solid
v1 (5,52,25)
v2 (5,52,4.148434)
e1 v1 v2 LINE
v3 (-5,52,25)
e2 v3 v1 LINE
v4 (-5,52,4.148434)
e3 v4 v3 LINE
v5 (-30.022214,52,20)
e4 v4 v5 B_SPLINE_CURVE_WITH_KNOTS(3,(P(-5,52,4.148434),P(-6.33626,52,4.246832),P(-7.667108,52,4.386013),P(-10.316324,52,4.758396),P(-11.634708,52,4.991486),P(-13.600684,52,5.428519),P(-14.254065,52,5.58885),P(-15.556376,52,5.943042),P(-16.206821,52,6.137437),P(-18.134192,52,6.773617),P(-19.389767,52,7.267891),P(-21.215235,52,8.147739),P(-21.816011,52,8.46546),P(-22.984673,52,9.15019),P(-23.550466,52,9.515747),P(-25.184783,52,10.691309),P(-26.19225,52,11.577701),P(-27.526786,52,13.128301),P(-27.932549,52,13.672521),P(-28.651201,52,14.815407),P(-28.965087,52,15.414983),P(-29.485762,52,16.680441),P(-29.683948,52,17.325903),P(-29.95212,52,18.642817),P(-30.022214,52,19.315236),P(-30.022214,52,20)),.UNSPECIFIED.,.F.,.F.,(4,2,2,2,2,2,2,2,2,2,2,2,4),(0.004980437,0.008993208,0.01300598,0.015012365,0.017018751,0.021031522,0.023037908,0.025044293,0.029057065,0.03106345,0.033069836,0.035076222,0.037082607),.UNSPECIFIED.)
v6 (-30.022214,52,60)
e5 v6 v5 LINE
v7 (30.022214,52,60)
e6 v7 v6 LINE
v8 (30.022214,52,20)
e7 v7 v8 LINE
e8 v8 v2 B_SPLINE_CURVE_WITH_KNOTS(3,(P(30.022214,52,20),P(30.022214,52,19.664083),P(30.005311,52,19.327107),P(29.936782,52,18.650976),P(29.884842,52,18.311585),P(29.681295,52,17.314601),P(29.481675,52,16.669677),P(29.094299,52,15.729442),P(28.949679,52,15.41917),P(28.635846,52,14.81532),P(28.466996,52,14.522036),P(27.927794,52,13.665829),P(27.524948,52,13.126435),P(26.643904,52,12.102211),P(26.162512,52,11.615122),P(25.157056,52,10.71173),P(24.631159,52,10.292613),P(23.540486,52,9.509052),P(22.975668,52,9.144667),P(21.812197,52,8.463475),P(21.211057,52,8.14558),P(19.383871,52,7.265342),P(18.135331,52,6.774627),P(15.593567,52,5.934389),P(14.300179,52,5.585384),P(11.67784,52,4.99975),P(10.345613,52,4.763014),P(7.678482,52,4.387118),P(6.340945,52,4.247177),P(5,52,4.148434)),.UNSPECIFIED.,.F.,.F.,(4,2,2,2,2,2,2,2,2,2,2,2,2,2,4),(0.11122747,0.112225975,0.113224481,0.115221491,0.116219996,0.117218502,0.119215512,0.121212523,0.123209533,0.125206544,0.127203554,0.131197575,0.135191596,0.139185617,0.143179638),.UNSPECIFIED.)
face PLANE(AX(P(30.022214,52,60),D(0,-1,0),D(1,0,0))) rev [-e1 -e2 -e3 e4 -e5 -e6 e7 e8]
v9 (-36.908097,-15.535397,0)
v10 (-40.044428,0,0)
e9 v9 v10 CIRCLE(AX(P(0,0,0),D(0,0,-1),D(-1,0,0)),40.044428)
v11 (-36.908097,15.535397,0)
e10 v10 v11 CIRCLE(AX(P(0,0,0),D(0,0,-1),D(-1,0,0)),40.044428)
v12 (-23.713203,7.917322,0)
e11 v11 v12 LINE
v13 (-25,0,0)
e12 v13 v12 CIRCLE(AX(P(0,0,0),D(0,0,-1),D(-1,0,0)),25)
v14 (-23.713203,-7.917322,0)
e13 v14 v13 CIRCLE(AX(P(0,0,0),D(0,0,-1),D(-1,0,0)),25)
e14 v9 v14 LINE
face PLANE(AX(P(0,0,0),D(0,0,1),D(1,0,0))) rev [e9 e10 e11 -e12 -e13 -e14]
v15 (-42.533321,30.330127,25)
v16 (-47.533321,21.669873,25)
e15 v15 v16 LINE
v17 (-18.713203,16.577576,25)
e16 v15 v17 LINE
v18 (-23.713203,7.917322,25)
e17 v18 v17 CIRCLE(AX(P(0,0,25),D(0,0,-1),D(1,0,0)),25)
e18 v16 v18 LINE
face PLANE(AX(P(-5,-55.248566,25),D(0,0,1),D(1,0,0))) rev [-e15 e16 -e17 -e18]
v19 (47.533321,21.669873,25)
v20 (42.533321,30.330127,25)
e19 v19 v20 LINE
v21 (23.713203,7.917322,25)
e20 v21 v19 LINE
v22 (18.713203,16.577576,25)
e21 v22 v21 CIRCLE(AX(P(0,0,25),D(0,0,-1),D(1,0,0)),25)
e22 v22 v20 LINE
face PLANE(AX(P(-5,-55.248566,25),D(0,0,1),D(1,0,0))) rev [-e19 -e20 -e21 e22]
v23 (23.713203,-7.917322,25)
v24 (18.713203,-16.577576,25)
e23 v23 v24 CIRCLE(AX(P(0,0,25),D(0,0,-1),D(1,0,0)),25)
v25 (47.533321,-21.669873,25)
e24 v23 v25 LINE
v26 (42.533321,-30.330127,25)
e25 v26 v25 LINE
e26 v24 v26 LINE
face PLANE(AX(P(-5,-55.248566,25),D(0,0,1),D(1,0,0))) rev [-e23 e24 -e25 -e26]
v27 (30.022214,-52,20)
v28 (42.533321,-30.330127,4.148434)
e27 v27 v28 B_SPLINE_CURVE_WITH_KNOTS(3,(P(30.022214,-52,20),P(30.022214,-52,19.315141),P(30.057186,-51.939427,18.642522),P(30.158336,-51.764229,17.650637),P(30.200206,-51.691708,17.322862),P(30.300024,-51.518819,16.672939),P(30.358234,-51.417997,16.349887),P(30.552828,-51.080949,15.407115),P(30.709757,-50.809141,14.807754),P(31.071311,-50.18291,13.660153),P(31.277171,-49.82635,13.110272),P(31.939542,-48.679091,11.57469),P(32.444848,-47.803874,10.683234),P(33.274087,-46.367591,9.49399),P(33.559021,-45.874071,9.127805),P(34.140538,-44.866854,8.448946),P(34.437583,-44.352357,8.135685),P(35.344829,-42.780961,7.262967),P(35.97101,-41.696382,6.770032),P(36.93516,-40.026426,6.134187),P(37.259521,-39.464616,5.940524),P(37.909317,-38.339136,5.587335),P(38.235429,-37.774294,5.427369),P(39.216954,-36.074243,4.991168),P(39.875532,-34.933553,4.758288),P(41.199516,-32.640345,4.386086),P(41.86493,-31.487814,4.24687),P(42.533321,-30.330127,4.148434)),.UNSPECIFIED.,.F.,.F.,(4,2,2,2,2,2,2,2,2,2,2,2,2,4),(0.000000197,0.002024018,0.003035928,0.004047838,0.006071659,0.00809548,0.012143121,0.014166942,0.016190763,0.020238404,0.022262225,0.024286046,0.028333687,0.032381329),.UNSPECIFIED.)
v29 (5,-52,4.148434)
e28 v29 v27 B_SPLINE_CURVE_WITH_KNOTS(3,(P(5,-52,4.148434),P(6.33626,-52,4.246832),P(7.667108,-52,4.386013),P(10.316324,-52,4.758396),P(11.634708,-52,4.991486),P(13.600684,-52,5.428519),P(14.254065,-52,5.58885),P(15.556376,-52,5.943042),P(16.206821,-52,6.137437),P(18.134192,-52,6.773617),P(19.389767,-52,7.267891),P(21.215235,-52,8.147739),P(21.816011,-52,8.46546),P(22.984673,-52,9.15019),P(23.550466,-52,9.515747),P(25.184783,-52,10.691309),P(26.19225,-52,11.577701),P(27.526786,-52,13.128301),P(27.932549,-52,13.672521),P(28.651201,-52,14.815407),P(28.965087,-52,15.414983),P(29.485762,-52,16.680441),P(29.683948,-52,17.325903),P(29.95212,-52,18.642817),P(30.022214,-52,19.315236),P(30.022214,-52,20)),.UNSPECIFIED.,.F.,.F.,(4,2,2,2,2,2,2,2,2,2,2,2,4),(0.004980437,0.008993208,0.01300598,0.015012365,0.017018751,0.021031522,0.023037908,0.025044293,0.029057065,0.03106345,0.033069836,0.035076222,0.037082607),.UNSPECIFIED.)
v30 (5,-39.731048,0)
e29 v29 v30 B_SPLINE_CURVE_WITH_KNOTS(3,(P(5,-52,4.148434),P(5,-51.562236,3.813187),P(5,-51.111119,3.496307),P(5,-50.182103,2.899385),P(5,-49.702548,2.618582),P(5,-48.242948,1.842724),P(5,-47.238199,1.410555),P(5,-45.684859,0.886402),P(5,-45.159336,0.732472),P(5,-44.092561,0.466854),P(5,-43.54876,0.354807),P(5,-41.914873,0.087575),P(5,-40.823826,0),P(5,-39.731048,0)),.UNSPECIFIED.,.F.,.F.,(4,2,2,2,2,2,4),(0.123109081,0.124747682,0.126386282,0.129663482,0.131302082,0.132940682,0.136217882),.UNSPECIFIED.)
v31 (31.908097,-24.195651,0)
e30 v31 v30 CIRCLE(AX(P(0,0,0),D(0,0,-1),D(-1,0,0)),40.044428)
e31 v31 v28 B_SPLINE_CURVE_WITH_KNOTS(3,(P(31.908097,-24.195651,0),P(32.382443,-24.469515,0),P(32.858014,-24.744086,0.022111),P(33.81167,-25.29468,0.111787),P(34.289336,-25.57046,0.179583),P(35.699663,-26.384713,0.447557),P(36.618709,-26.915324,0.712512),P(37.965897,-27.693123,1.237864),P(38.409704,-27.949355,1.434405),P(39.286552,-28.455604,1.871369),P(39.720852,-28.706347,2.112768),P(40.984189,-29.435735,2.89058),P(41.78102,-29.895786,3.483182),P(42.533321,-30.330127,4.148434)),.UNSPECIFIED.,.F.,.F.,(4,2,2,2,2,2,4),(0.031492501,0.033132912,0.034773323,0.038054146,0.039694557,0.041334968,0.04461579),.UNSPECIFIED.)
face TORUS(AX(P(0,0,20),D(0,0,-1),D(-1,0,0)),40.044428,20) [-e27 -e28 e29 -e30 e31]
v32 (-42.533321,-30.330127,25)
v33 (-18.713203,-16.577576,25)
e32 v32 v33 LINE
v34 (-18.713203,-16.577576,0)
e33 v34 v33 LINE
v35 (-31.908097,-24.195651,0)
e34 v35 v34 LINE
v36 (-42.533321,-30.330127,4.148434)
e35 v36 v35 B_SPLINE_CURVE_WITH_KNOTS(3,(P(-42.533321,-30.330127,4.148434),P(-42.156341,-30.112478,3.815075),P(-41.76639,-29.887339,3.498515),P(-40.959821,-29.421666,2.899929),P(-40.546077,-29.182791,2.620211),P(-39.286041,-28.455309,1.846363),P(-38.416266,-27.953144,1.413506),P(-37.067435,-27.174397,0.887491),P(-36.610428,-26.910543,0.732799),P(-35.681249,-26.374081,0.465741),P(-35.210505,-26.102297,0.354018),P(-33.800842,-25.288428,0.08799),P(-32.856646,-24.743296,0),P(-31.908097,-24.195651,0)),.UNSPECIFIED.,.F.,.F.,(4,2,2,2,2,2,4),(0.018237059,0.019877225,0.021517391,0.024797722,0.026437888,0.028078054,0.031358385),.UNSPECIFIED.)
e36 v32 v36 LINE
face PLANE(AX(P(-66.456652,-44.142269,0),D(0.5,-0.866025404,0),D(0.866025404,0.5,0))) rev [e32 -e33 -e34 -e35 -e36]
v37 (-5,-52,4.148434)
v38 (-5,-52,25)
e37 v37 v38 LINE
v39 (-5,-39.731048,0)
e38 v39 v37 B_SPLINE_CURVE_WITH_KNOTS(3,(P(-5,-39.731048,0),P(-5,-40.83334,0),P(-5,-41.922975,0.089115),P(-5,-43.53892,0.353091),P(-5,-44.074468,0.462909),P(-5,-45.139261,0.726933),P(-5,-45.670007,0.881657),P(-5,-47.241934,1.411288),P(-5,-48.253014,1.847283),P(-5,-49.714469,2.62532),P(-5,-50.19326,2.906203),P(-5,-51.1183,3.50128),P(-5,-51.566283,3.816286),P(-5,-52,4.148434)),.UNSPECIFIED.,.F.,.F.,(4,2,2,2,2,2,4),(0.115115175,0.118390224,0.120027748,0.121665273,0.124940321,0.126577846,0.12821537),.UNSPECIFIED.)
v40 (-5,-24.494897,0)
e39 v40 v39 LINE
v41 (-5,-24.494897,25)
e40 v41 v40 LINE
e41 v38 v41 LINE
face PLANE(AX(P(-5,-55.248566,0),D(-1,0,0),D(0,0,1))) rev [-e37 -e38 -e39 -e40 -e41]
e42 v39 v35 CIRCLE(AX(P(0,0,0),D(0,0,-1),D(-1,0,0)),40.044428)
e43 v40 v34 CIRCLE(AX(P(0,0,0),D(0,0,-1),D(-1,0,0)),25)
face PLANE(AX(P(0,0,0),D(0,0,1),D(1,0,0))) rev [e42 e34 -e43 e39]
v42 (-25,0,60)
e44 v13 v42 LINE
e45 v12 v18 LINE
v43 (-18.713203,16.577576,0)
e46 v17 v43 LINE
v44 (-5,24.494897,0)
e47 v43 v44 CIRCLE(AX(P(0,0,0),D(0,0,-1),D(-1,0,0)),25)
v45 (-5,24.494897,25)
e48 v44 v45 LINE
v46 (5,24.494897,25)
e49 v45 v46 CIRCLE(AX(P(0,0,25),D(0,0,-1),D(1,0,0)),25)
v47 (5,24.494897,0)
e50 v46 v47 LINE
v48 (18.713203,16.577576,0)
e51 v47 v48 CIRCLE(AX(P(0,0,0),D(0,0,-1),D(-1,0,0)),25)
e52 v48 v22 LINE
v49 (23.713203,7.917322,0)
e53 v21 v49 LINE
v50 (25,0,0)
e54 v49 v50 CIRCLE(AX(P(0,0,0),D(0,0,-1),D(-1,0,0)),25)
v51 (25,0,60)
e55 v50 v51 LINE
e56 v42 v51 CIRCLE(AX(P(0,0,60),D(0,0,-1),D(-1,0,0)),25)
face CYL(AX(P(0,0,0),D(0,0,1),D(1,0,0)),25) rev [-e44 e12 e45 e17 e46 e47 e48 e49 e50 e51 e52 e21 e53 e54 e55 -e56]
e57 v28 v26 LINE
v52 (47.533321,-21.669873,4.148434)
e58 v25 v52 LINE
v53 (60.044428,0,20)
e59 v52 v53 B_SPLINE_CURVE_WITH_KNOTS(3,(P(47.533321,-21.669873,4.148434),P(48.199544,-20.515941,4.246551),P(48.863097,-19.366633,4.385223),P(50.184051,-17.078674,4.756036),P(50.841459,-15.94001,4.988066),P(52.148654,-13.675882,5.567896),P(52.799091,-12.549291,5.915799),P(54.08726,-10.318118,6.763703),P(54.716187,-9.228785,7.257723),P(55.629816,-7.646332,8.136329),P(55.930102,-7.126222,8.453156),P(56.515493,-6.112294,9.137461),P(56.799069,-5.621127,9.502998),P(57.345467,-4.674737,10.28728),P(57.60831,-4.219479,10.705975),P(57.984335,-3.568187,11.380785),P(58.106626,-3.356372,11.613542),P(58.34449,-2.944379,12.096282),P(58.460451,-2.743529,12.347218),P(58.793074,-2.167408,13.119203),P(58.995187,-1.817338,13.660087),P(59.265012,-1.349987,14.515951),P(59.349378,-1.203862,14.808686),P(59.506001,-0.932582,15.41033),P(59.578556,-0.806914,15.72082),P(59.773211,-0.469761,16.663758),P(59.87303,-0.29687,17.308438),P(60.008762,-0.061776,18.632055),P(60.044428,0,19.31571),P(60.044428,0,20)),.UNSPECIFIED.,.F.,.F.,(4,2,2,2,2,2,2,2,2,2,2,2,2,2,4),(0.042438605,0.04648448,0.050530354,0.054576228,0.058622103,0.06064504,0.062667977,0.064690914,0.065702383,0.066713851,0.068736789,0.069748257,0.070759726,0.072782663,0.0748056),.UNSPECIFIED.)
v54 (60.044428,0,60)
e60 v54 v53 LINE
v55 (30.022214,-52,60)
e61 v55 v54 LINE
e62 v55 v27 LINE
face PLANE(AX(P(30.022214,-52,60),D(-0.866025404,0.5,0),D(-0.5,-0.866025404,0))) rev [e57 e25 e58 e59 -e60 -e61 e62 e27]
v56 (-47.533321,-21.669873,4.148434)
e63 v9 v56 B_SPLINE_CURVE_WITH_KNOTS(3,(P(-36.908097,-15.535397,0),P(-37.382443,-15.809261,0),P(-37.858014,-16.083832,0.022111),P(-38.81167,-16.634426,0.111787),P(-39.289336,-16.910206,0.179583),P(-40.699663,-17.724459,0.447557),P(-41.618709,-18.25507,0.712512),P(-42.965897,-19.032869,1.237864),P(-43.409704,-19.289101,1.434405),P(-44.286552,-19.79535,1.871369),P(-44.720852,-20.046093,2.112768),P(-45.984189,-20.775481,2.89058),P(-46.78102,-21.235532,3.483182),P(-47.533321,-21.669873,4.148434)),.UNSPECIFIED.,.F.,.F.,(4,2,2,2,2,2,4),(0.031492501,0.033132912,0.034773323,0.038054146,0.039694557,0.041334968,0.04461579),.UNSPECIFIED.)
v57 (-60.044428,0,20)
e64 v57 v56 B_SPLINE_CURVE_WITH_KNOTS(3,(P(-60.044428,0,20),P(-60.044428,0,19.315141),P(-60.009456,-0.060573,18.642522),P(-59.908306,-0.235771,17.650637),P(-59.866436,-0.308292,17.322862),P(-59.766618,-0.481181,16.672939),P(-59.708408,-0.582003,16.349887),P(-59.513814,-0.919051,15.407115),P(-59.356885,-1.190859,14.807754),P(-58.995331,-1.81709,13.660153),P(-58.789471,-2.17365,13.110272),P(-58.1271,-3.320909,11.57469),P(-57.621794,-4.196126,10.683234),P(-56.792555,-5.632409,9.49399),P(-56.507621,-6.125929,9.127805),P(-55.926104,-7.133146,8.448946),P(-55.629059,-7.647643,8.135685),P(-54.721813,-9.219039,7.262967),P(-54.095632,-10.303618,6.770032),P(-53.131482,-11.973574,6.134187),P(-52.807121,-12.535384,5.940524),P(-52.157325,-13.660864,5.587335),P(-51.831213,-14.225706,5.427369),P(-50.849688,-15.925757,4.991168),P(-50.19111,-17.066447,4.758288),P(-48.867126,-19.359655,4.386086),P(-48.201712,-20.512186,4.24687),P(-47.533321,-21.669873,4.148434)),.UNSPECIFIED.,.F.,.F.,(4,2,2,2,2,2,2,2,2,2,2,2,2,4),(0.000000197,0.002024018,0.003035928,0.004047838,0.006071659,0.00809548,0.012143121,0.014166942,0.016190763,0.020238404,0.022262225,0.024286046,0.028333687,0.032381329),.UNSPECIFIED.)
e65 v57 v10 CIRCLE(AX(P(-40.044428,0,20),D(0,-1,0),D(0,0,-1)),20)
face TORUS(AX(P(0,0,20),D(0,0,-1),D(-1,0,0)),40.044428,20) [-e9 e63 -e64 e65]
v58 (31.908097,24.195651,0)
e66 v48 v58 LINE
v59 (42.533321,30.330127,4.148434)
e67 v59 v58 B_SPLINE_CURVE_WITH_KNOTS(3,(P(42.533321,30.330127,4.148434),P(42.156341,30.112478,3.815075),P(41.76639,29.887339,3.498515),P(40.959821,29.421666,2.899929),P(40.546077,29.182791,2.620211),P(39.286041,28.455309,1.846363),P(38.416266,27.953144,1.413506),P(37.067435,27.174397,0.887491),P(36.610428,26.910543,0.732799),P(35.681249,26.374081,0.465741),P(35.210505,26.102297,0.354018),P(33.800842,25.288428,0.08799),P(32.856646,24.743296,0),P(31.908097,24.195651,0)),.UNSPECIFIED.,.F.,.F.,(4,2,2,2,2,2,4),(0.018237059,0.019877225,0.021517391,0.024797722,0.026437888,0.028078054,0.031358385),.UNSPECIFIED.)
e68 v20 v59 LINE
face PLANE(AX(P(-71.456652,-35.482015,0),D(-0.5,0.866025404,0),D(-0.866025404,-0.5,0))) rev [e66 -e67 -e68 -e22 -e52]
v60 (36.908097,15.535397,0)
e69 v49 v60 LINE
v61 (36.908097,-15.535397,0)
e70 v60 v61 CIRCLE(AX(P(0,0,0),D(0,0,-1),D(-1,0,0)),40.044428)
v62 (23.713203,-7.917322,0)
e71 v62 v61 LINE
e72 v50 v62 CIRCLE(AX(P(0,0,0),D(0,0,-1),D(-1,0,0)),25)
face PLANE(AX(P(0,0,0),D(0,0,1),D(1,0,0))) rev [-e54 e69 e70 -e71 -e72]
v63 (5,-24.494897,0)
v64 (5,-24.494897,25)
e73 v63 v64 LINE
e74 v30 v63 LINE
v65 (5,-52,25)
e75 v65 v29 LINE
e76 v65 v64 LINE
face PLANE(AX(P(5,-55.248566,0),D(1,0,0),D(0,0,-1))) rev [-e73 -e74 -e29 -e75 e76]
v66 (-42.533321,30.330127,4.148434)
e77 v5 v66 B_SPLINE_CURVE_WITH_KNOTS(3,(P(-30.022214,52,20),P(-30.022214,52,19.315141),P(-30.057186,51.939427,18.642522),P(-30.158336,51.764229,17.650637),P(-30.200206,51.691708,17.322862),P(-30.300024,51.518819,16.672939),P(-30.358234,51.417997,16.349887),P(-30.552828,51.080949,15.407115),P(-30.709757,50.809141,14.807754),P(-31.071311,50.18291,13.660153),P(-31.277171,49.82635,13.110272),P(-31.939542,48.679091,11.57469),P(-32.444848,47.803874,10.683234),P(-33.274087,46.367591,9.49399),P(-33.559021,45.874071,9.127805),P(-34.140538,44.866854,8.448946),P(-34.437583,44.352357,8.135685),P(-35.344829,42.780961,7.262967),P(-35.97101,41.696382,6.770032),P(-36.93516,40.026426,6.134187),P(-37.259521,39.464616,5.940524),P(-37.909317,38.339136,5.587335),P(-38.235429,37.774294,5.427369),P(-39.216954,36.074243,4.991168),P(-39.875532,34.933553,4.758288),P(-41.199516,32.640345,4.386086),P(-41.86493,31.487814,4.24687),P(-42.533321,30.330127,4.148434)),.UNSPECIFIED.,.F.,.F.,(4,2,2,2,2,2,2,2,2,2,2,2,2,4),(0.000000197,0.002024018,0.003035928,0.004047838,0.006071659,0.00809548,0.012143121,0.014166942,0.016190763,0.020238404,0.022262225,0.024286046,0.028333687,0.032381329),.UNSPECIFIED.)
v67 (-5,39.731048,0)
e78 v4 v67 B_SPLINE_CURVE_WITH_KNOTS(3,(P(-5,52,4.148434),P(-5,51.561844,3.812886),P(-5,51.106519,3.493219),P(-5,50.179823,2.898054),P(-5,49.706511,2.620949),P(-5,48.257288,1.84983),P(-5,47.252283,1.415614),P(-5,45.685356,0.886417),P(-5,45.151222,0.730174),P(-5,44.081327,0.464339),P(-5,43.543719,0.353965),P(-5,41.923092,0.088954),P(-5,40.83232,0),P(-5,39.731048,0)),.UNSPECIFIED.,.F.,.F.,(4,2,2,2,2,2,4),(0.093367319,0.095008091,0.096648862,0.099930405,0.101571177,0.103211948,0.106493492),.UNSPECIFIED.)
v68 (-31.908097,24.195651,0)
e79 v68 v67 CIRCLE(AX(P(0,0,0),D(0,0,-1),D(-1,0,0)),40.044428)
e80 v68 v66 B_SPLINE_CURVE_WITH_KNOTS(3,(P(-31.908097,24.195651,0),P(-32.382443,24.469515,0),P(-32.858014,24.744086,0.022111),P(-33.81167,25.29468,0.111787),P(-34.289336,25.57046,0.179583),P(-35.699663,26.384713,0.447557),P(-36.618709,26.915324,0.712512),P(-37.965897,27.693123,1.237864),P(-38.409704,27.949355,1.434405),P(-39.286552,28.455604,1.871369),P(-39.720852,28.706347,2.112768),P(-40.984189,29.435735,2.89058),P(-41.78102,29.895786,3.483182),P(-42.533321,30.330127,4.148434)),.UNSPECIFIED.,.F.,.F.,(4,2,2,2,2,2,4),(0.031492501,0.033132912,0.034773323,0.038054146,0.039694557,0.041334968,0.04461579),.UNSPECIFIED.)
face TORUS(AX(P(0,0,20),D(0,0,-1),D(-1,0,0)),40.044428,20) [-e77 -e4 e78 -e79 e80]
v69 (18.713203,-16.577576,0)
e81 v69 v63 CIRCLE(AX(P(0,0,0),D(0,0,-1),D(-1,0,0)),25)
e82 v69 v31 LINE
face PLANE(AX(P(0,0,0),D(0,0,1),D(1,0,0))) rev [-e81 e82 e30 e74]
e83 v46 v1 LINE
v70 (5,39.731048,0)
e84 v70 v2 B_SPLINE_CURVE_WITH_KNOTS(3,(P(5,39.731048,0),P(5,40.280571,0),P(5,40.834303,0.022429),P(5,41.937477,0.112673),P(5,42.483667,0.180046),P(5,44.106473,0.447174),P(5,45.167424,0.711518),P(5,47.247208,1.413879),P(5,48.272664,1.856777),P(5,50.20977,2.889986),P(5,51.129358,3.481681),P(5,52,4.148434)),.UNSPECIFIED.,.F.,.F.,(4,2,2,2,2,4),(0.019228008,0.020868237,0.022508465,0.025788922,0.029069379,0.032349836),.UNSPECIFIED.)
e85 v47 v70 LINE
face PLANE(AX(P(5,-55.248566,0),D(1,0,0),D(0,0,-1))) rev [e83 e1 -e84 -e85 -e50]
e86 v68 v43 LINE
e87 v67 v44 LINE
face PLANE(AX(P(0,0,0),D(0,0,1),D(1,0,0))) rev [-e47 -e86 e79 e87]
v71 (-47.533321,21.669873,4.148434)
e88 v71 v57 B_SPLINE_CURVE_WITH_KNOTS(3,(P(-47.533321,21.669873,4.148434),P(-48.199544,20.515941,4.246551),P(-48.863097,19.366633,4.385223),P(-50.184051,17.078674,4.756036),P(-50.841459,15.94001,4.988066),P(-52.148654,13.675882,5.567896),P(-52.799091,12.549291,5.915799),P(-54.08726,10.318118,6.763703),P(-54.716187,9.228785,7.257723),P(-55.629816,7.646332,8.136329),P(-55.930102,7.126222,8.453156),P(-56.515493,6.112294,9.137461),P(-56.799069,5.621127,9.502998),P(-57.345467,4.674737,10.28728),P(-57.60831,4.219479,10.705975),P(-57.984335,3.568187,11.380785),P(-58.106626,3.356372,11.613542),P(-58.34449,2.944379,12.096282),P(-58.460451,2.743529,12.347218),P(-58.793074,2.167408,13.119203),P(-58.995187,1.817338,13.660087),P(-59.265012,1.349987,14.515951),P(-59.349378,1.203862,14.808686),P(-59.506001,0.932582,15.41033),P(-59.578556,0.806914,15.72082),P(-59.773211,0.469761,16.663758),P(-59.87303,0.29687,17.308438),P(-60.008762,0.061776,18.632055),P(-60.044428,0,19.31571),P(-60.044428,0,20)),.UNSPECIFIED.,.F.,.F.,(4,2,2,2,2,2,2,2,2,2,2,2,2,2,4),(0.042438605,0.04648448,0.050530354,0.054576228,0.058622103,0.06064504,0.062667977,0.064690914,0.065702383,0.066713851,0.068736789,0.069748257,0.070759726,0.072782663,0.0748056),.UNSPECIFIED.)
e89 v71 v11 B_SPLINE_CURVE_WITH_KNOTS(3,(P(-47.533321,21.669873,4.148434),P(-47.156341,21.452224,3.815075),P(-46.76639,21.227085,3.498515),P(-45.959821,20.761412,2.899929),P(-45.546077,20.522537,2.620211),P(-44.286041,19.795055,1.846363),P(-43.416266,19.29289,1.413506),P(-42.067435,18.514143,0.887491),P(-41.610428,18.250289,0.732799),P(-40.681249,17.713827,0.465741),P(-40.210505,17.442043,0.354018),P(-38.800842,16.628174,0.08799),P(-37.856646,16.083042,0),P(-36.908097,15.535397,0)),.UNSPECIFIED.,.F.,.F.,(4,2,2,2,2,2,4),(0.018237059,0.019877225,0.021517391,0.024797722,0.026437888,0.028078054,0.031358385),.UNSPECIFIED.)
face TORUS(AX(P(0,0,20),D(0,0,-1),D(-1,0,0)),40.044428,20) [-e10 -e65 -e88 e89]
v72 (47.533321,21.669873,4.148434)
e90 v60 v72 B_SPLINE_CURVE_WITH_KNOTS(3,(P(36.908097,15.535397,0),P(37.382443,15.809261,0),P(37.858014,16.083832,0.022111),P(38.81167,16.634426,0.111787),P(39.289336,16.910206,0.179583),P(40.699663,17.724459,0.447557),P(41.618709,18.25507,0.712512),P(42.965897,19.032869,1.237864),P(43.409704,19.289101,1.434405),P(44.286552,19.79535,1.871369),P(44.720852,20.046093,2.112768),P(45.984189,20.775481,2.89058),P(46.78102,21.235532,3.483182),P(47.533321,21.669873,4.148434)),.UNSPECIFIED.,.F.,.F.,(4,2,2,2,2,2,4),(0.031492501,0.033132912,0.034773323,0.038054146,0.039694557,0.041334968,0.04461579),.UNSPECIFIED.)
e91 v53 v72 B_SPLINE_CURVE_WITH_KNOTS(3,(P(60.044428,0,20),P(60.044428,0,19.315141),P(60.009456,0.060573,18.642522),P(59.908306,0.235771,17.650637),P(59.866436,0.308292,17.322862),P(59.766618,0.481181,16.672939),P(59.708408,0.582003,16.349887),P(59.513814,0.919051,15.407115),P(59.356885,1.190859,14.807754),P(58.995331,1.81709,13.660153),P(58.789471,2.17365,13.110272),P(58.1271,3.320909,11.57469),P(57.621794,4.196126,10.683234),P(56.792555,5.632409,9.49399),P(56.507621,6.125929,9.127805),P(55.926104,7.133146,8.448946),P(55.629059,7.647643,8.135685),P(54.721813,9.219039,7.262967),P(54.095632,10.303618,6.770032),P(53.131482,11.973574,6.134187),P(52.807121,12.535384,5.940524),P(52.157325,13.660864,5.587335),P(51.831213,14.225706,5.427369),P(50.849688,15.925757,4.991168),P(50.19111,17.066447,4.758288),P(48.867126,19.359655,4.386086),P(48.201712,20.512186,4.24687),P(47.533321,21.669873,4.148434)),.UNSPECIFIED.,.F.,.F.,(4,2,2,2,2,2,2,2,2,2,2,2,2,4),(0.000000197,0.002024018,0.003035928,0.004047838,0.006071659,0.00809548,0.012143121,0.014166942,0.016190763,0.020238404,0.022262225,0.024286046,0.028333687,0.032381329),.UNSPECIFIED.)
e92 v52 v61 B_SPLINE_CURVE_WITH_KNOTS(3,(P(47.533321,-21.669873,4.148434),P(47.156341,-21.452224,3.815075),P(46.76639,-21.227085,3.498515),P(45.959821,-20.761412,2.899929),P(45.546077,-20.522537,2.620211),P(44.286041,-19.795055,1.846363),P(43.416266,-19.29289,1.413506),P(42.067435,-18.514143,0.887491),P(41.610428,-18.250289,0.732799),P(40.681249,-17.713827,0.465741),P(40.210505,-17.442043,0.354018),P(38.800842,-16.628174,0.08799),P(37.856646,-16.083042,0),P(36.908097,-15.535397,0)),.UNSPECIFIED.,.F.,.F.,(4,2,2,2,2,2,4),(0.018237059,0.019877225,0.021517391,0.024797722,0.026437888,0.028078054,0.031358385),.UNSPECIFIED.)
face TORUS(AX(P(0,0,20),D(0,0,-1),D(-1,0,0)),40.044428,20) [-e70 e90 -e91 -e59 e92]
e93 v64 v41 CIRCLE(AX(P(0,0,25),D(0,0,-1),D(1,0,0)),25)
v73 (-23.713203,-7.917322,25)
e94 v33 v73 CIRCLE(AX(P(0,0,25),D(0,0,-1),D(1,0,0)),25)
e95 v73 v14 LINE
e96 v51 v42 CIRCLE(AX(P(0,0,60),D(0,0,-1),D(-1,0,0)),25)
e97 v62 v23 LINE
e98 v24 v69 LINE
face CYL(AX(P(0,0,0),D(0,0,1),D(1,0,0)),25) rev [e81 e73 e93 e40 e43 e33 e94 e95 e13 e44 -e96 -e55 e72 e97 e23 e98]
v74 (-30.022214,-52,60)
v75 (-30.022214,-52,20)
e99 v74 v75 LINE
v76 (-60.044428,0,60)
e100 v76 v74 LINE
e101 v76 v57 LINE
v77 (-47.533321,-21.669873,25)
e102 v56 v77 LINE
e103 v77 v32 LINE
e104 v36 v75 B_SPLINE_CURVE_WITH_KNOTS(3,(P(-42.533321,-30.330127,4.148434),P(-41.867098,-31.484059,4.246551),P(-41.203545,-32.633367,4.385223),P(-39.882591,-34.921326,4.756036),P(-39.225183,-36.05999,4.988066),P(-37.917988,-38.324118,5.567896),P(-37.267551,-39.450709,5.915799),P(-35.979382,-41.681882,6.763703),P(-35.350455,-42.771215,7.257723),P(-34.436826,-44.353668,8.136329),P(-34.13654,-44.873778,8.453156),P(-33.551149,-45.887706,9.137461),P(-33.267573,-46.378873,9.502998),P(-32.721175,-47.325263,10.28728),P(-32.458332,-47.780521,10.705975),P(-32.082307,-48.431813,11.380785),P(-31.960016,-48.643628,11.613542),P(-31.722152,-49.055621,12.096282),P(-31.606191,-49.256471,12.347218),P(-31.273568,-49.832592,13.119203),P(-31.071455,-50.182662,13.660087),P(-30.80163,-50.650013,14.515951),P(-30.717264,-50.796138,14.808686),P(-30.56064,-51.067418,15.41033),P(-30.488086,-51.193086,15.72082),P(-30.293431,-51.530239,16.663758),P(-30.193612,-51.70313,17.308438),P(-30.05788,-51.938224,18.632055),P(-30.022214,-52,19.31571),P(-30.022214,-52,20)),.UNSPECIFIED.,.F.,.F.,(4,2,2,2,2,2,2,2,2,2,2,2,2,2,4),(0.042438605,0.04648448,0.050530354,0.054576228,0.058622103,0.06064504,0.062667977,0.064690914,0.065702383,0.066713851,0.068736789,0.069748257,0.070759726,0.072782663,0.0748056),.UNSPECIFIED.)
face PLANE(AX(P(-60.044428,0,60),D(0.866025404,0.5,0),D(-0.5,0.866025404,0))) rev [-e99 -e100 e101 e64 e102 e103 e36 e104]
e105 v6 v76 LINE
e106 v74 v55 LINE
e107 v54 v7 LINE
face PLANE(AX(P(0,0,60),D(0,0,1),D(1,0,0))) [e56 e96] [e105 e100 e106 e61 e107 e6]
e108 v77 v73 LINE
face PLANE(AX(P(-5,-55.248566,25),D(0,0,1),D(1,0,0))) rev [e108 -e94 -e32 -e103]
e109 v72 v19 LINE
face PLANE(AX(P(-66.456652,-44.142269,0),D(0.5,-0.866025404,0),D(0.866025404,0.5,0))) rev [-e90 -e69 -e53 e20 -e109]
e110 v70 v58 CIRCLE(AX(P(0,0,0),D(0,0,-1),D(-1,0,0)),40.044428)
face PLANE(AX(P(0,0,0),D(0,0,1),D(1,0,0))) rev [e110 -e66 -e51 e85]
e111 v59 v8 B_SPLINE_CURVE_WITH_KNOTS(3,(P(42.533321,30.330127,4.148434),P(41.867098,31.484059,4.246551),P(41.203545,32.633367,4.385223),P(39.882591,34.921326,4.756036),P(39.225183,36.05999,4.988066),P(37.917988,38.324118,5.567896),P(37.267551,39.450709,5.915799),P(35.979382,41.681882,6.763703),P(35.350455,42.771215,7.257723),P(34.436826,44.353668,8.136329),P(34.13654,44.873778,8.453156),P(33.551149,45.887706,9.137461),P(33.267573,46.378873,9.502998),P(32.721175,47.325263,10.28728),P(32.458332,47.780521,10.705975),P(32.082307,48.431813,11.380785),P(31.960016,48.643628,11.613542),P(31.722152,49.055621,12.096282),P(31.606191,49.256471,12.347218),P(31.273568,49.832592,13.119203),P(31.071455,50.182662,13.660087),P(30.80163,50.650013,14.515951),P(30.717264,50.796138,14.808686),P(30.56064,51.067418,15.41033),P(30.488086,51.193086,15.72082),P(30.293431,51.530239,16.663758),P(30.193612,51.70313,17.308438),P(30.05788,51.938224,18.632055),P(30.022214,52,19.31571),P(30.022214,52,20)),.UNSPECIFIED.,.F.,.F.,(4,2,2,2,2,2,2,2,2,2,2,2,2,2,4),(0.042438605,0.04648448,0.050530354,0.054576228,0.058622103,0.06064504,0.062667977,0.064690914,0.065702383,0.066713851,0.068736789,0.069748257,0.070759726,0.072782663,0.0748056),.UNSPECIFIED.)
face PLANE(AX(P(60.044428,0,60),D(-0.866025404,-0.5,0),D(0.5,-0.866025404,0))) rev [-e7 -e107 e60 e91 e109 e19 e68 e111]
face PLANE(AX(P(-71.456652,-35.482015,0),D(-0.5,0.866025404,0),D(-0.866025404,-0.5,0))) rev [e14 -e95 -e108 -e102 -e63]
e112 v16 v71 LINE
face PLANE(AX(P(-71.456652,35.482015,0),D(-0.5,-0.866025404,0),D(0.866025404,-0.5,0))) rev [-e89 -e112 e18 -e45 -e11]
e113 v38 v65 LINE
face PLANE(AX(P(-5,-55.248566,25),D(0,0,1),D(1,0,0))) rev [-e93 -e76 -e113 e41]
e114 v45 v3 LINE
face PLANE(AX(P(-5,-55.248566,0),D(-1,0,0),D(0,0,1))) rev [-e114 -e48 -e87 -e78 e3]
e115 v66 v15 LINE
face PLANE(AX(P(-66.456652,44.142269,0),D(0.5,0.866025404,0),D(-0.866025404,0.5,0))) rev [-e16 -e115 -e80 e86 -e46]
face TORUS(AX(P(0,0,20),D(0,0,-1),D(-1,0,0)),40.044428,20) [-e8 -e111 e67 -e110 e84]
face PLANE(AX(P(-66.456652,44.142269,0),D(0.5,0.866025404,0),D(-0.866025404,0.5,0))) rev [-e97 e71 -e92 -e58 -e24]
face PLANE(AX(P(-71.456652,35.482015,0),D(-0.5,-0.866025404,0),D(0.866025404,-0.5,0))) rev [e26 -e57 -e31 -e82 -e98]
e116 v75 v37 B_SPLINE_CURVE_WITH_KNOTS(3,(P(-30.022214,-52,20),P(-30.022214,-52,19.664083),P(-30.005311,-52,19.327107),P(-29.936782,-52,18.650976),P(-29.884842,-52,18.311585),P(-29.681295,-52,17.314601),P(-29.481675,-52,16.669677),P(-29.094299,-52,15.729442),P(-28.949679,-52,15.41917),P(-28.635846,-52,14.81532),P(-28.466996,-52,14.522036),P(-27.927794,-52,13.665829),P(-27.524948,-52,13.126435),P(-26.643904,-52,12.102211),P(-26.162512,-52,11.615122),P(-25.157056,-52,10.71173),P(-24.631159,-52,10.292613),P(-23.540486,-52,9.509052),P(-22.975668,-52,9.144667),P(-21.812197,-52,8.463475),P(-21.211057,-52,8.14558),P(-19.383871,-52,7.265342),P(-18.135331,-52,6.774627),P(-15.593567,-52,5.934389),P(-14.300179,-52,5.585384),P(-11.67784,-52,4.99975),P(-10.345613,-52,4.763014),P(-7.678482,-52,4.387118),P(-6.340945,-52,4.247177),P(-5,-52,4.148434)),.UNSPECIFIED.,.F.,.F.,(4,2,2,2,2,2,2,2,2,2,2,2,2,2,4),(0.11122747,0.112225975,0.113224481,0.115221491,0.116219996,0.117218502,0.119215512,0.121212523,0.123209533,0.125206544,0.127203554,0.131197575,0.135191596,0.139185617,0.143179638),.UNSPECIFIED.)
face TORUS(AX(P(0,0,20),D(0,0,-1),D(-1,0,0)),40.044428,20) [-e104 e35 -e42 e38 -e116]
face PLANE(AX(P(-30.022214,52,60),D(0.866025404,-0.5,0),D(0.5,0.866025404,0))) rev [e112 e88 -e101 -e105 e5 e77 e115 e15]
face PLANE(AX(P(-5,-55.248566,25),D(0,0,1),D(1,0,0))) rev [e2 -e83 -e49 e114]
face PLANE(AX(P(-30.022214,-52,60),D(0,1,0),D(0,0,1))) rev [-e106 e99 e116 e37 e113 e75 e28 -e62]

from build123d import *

# Parameters (mm, degrees)
BOSS_EXTRUDE1_DEPTH     = 60
SKETCH3_W               = 10
SKETCH3_H               = 25
CUT_EXTRUDE1_DEPTH      = 135.243559913
CIRPATTERN1_COUNT       = 6
CUT_EXTRUDE2_DEPTH      = 87.800537803
CUT_EXTRUDE2_DEPTH_BACK = 87.800537803
SKETCH4_R               = 25


with BuildPart() as part:
    # Sketch1 → Boss-Extrude1 (new body)
    with BuildSketch(Plane.XY):
        Polygon((30.022213998, -52), (60.044427996, 0), (30.022213998, 52), (-30.022213998, 52), (-60.044427996, 0), (-30.022213998, -52), align=None)
    extrude(amount=BOSS_EXTRUDE1_DEPTH)

    # Sketch2 → Cut-Revolve1 (revolve, cut)
    with BuildSketch(Plane(origin=(0, 0, 0), x_dir=(1, 0, 0), z_dir=(0, 1, 0))):
        with BuildLine():
            Line((-60.044427996, -20), (-60.044427996, 0))
            Line((-60.044427996, 0), (-40.044427996, 0))
            ThreePointArc((-40.044427996, 0), (-54.186563619, -5.857864376), (-60.044427996, -20))
        make_face()
    revolve(axis=Axis((0, 0, -15.505085141), (0, 0, 1)), mode=Mode.SUBTRACT)

    # Sketch3 → Cut-Extrude1 (cut, through all)
    with BuildSketch(Plane(origin=(0, 52, 0), x_dir=(1, 0, 0), z_dir=(0, 1, 0))):
        with Locations((0, -12.5)):
            Rectangle(SKETCH3_W, SKETCH3_H)
    cut_extrude1 = extrude(amount=-CUT_EXTRUDE1_DEPTH, mode=Mode.SUBTRACT)

    # CirPattern1: Cut-Extrude1 ×6 about axis
    cirpattern1_axis = Axis((0, 0, 0), (0, 0, 1))
    for i in range(1, CIRPATTERN1_COUNT):
        add(cut_extrude1.rotate(cirpattern1_axis, i * 360 / CIRPATTERN1_COUNT), mode=Mode.SUBTRACT)

    # Sketch4 → Cut-Extrude2 (cut, two sides: drawn at the far end of the back side and taken through both)
    with BuildSketch(Plane(origin=(0, 0, 25), x_dir=(-1, 0, 0), z_dir=(0, 0, -1)).offset(-CUT_EXTRUDE2_DEPTH_BACK)):
        with Locations(Location((0, 0, 0), (0, 0, 161.536959033))):
            Circle(SKETCH4_R)
    extrude(amount=CUT_EXTRUDE2_DEPTH + CUT_EXTRUDE2_DEPTH_BACK, mode=Mode.SUBTRACT)


solid = part.part
